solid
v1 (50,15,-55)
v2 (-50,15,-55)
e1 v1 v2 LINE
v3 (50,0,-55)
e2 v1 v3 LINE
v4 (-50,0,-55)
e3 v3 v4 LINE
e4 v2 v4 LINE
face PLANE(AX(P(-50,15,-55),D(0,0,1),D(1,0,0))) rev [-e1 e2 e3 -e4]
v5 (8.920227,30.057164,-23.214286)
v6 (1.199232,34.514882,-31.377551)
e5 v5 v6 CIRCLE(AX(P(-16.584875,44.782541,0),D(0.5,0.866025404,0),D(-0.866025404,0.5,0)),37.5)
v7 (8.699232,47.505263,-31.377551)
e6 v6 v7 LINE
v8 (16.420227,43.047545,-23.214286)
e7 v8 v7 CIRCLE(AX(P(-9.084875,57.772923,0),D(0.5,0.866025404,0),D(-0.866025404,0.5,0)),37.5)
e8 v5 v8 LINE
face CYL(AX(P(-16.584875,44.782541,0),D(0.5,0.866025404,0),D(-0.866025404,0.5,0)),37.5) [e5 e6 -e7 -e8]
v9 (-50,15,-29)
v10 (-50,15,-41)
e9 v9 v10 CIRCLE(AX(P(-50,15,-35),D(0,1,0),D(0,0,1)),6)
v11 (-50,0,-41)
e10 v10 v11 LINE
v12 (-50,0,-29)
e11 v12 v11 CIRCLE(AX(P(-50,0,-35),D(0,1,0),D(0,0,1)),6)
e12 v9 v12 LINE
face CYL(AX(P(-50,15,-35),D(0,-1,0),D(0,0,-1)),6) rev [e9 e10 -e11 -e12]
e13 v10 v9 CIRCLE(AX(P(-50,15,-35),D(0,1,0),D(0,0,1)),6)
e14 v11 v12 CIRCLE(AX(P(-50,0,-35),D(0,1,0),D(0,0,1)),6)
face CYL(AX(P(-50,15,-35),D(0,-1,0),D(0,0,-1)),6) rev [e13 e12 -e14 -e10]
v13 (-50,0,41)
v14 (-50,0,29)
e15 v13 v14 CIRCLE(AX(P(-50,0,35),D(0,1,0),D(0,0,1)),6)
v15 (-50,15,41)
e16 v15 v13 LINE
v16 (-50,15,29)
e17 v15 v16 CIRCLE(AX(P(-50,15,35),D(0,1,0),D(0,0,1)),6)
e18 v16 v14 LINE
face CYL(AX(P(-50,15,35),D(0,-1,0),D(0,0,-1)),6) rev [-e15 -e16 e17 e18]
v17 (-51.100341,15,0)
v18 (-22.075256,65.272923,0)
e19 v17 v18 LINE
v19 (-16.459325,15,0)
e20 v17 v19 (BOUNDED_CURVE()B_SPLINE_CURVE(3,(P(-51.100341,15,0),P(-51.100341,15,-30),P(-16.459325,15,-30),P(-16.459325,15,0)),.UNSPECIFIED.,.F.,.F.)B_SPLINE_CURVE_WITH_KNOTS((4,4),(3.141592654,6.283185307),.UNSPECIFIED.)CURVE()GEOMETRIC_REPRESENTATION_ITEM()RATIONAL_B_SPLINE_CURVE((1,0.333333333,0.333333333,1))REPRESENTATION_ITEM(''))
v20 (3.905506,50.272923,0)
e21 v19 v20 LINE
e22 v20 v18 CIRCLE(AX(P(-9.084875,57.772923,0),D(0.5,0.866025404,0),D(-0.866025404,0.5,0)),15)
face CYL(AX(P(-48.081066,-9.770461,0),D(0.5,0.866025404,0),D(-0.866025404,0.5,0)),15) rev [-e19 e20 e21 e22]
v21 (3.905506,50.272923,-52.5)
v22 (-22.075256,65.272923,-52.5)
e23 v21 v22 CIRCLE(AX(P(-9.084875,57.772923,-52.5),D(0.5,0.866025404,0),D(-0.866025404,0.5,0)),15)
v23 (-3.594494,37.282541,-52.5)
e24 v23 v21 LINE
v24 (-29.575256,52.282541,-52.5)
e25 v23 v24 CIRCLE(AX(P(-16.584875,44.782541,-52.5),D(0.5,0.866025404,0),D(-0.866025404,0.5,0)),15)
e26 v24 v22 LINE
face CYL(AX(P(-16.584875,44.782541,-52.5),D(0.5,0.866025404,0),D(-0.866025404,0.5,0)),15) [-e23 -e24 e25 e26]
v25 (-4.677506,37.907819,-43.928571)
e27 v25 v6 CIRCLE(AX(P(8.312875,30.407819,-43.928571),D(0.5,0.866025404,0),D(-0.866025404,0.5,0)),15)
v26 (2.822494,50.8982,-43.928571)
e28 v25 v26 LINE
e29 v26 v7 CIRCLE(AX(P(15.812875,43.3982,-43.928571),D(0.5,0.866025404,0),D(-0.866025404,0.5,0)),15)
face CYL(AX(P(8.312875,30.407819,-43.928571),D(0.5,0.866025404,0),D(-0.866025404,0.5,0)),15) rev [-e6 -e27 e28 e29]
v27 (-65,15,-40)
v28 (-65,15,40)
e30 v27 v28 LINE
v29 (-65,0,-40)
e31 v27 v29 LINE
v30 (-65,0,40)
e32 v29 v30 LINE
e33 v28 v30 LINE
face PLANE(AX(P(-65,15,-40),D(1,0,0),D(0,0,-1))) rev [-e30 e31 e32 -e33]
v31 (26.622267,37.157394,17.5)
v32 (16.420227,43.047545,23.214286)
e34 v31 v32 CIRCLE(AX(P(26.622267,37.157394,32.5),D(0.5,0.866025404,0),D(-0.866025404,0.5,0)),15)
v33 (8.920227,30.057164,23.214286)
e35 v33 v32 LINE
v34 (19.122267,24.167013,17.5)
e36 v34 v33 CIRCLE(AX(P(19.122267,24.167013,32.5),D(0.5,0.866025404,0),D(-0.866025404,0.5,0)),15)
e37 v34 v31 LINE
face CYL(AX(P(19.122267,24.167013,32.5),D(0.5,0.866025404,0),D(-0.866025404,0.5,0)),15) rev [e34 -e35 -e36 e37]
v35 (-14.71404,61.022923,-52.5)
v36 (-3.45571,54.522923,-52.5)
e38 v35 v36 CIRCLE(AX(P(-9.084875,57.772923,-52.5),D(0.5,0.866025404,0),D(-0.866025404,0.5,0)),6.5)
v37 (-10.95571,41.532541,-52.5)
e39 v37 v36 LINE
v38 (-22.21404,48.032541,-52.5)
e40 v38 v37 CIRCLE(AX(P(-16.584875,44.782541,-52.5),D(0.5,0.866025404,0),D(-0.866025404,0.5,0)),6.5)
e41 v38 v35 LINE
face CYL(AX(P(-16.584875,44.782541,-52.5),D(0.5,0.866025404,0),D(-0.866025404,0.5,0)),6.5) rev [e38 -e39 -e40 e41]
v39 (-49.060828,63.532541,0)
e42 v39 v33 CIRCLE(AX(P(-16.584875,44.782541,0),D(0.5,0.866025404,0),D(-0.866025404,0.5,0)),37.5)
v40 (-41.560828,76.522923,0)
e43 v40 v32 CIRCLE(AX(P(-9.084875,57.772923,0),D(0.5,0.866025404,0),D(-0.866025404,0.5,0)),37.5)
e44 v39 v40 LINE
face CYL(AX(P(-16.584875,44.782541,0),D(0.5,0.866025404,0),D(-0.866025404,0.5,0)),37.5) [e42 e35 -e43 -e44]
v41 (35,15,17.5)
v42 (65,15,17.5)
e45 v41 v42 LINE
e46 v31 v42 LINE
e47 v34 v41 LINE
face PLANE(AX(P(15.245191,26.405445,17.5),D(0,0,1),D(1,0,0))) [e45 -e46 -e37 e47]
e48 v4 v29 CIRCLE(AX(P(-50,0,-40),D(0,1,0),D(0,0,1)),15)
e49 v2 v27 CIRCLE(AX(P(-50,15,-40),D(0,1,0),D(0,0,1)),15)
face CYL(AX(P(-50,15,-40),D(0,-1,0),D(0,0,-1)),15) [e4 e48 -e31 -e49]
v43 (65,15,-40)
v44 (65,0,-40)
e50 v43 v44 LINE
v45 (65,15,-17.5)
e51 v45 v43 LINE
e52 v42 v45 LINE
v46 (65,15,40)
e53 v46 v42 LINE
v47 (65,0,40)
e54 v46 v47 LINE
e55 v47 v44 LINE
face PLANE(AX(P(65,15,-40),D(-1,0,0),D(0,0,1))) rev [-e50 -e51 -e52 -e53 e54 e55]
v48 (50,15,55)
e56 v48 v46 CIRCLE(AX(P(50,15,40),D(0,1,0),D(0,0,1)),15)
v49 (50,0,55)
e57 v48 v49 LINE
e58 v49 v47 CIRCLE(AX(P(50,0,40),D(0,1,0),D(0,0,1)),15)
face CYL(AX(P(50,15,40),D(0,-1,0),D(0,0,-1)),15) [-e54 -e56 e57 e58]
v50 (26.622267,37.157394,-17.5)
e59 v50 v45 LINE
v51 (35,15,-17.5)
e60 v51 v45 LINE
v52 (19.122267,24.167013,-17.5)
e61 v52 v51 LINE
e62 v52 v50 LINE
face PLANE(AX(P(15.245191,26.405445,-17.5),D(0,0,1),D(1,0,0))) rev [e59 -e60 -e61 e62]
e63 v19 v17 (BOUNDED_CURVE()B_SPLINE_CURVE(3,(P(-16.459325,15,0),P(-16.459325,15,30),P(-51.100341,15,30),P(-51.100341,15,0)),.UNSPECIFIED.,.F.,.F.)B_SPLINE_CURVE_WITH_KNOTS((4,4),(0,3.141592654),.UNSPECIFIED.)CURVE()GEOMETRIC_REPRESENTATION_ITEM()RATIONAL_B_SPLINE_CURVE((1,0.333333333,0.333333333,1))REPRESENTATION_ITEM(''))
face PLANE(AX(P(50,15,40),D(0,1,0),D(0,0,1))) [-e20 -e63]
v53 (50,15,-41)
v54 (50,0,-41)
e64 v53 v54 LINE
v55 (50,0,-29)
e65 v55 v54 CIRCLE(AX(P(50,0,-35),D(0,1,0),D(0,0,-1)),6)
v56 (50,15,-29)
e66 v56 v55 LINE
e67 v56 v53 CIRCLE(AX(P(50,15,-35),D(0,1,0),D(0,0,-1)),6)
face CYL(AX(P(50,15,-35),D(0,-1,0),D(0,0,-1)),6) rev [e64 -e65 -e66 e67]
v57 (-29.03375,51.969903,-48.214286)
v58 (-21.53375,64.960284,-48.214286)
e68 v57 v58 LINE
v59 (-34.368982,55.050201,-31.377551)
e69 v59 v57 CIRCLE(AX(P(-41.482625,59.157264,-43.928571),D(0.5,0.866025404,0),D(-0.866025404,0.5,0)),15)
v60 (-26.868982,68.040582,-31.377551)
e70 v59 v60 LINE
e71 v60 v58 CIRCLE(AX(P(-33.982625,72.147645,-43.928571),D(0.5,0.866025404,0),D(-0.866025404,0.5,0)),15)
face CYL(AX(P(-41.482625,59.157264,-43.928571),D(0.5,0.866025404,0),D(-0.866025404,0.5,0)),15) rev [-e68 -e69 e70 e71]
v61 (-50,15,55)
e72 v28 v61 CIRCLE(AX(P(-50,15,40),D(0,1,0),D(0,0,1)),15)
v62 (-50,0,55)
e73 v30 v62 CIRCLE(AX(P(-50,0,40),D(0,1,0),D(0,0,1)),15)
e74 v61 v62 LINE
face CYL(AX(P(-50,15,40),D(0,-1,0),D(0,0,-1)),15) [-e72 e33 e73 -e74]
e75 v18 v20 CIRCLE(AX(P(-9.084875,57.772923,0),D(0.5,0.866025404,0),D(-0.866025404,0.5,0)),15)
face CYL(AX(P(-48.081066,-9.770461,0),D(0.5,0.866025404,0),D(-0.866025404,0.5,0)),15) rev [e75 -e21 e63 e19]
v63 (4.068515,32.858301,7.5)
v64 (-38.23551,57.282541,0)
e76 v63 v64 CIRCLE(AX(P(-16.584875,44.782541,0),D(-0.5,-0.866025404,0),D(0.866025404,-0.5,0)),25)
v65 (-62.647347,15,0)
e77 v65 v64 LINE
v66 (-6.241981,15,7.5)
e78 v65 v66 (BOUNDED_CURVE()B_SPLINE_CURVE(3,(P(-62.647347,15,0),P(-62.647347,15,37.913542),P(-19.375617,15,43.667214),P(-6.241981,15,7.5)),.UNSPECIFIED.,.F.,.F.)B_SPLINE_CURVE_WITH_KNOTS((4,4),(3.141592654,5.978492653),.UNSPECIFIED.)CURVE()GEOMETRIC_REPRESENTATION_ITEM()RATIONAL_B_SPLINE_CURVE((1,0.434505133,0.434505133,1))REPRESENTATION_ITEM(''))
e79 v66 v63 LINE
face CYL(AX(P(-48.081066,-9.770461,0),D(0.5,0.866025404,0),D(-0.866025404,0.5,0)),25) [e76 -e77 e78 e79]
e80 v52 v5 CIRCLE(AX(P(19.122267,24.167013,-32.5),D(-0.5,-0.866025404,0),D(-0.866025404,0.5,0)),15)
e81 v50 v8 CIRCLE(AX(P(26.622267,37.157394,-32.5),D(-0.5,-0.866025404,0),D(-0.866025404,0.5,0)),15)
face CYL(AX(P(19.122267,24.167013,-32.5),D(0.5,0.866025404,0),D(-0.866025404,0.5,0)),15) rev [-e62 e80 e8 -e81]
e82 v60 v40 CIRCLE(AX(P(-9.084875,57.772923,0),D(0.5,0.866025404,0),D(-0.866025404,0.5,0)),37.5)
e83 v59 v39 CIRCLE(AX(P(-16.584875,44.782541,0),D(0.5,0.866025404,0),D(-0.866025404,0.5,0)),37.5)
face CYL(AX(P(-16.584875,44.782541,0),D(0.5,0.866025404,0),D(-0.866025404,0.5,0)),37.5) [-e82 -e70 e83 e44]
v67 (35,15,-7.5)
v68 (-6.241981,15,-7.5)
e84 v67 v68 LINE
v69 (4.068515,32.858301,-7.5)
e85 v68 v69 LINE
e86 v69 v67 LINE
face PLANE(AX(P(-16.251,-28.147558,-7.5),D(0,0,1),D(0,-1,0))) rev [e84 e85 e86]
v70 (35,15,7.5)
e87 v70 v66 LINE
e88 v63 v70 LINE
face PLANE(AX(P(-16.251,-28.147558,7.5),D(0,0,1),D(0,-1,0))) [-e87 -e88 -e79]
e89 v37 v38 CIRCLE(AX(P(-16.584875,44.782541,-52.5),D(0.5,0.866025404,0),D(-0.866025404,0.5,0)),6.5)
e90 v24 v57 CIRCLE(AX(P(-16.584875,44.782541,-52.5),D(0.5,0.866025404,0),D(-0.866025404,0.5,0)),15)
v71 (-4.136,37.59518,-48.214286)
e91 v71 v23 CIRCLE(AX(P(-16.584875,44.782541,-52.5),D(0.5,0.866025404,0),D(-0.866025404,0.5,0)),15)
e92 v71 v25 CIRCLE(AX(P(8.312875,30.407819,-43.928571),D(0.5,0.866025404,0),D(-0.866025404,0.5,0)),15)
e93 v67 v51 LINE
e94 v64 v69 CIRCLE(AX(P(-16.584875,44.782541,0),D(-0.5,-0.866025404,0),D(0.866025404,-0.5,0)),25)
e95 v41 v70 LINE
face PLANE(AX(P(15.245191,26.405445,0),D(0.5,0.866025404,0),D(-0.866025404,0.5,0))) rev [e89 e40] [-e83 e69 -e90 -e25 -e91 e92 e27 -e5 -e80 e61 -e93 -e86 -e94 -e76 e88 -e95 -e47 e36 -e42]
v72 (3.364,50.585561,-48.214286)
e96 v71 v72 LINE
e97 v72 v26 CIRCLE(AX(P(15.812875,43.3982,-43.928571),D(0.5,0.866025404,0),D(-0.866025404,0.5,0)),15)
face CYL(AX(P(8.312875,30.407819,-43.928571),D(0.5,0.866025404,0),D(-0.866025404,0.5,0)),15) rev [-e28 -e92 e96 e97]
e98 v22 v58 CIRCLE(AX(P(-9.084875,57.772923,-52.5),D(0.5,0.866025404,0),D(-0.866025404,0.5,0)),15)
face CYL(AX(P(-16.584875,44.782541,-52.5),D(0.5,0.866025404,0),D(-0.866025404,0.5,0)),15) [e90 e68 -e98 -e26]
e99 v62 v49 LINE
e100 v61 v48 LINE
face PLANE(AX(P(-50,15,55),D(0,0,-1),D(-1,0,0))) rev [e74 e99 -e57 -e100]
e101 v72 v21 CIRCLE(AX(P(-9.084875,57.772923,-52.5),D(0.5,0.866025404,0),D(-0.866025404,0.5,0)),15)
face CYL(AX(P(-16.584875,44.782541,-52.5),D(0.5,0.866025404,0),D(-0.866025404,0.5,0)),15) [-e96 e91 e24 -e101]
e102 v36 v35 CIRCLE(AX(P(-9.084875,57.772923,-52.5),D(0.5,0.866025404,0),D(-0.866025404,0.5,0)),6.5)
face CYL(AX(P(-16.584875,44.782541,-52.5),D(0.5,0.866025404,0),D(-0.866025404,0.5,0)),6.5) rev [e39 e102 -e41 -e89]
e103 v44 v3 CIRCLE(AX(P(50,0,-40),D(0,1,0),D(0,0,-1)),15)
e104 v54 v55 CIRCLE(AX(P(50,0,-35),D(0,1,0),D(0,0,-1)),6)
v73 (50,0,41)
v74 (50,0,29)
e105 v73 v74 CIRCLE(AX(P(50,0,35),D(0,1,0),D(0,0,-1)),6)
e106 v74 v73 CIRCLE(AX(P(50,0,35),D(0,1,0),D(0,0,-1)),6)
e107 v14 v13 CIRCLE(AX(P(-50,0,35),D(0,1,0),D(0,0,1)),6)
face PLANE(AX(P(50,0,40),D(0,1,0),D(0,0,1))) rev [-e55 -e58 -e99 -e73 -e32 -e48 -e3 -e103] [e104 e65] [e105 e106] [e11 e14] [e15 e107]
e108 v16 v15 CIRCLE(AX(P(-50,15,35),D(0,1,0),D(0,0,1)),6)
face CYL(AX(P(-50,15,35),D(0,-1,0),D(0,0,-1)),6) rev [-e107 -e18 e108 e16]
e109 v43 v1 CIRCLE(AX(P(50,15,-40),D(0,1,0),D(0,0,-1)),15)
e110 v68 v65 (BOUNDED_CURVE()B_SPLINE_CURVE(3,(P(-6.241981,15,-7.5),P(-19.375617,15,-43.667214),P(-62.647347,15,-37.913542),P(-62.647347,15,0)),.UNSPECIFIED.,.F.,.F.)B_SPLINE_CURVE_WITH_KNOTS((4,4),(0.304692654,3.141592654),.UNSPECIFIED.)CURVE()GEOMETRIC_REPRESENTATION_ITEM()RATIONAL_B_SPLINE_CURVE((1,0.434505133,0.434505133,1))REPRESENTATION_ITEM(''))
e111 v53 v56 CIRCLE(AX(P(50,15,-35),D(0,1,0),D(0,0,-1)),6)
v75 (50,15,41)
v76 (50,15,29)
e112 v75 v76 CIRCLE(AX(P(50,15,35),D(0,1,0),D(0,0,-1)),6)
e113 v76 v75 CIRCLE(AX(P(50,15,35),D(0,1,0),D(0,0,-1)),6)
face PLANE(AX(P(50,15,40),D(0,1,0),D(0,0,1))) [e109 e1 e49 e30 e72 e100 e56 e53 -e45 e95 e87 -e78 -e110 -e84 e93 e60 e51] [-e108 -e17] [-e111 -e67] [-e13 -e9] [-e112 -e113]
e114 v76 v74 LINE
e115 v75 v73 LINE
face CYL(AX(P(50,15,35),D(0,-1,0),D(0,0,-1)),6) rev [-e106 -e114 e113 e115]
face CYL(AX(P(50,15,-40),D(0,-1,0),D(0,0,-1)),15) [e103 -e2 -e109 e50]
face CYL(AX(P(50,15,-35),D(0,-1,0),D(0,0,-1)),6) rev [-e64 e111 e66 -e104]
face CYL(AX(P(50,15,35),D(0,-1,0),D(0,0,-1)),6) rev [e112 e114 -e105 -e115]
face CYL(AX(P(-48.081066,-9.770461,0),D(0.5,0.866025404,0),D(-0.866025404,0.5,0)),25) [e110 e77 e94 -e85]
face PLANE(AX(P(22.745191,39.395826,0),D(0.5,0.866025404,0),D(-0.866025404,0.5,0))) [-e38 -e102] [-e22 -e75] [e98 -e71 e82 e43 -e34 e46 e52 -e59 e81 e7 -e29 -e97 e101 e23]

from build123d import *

# Parameters (mm, degrees)
BASE_PLATE_SKETCH_R     = 6
BASE_PLATE_DEPTH        = 15
INCLINED_ARM_SKETCH_R   = 15
INCLINED_ARM_SKETCH_R_2 = 6.5
INCLINED_ARM_DEPTH      = 15
LUG_WITH_BORE_REACH     = 118.221
LUG_SKETCH_R            = 15


with BuildPart() as part:
    # Base Plate Sketch → Base Plate (new body)
    with BuildSketch(Plane(origin=(0, 0, 0), x_dir=(1, 0, 0), z_dir=(0, 1, 0))):
        with BuildLine():
            Line((-50, 55), (50, 55))
            ThreePointArc((50, 55), (60.606601718, 50.606601718), (65, 40))
            Line((65, 40), (65, -40))
            ThreePointArc((65, -40), (60.606601718, -50.606601718), (50, -55))
            Line((50, -55), (-50, -55))
            ThreePointArc((-50, -55), (-60.606601718, -50.606601718), (-65, -40))
            Line((-65, -40), (-65, 40))
            ThreePointArc((-65, 40), (-60.606601718, 50.606601718), (-50, 55))
        make_face()
        with Locations(Location((-50, 35, 0), (0, 0, 270))):
            Circle(BASE_PLATE_SKETCH_R, mode=Mode.SUBTRACT)
        with Locations(Location((-50, -35, 0), (0, 0, 270))):
            Circle(BASE_PLATE_SKETCH_R, mode=Mode.SUBTRACT)
        with Locations(Location((50, -35, 0), (0, 0, 90))):
            Circle(BASE_PLATE_SKETCH_R, mode=Mode.SUBTRACT)
        with Locations(Location((50, 35, 0), (0, 0, 90))):
            Circle(BASE_PLATE_SKETCH_R, mode=Mode.SUBTRACT)
    extrude(amount=BASE_PLATE_DEPTH)

    # Lug Sketch → Lug with Bore (add, up to next)
    with BuildSketch(Plane(origin=(15.245190528, 26.405444566, 0), x_dir=(0.8660254037844417, -0.4999999999999947, 0), z_dir=(-0.4999999999999947, -0.8660254037844417, 0)), mode=Mode.PRIVATE) as lug_with_bore_sk1:
        with BuildLine():
            ThreePointArc((-12.905713736, 7.5), (-61.754193771, 0), (-12.905713736, -7.5))
            Line((-12.905713736, -7.5), (48.791651246, -7.5))
            Line((48.791651246, -7.5), (48.791651246, 7.5))
            Line((48.791651246, 7.5), (-12.905713736, 7.5))
        make_face()
        with Locations(Location((-36.754193771, 0, 0), (0, 0, 180))):
            Circle(LUG_SKETCH_R, mode=Mode.SUBTRACT)
    lug_with_bore_tool1 = extrude(lug_with_bore_sk1.sketch, amount=LUG_WITH_BORE_REACH, mode=Mode.PRIVATE) - part.part


with BuildPart() as body_2:
    # Inclined Arm Sketch → Inclined Arm (new body)
    with BuildSketch(Plane(origin=(22.745190528, 39.395825623, 0), x_dir=(-0.8660254037844417, 0.4999999999999947, 0), z_dir=(0.4999999999999947, 0.8660254037844417, 0))):
        with BuildLine():
            Line((-4.476862485, 17.5), (-48.791651246, 17.5))
            Line((-48.791651246, 17.5), (-48.791651246, -17.5))
            Line((-48.791651246, -17.5), (-4.476862485, -17.5))
            ThreePointArc((-4.476862485, -17.5), (2.069674222, -19.003968837), (7.303439302, -23.214285714))
            ThreePointArc((7.303439302, -23.214285714), (11.430063197, -27.657519966), (16.21887561, -31.37755102))
            ThreePointArc((16.21887561, -31.37755102), (22.091371242, -38.774247477), (22.379471059, -48.214285714))
            ThreePointArc((22.379471059, -48.214285714), (36.754193771, -67.5), (51.128916484, -48.214285714))
            ThreePointArc((51.128916484, -48.214285714), (51.4170163, -38.774247477), (57.289511932, -31.37755102))
            ThreePointArc((57.289511932, -31.37755102), (64.411713737, 25.324130574), (7.303439302, 23.214285714))
            ThreePointArc((7.303439302, 23.214285714), (2.069674222, 19.003968837), (-4.476862485, 17.5))
        make_face()
        with Locations((36.754193771, 0)):
            Circle(INCLINED_ARM_SKETCH_R, mode=Mode.SUBTRACT)
        with Locations((36.754193771, -52.5)):
            Circle(INCLINED_ARM_SKETCH_R_2, mode=Mode.SUBTRACT)
    extrude(amount=-INCLINED_ARM_DEPTH)


with BuildPart() as part_1:
    add(part.part)

    add(body_2.part)  # Lug with Bore merges body 2
    add(lug_with_bore_tool1.solids().sort_by_distance((3.499955, 33.18656, 0))[0])


solid = part_1.part
